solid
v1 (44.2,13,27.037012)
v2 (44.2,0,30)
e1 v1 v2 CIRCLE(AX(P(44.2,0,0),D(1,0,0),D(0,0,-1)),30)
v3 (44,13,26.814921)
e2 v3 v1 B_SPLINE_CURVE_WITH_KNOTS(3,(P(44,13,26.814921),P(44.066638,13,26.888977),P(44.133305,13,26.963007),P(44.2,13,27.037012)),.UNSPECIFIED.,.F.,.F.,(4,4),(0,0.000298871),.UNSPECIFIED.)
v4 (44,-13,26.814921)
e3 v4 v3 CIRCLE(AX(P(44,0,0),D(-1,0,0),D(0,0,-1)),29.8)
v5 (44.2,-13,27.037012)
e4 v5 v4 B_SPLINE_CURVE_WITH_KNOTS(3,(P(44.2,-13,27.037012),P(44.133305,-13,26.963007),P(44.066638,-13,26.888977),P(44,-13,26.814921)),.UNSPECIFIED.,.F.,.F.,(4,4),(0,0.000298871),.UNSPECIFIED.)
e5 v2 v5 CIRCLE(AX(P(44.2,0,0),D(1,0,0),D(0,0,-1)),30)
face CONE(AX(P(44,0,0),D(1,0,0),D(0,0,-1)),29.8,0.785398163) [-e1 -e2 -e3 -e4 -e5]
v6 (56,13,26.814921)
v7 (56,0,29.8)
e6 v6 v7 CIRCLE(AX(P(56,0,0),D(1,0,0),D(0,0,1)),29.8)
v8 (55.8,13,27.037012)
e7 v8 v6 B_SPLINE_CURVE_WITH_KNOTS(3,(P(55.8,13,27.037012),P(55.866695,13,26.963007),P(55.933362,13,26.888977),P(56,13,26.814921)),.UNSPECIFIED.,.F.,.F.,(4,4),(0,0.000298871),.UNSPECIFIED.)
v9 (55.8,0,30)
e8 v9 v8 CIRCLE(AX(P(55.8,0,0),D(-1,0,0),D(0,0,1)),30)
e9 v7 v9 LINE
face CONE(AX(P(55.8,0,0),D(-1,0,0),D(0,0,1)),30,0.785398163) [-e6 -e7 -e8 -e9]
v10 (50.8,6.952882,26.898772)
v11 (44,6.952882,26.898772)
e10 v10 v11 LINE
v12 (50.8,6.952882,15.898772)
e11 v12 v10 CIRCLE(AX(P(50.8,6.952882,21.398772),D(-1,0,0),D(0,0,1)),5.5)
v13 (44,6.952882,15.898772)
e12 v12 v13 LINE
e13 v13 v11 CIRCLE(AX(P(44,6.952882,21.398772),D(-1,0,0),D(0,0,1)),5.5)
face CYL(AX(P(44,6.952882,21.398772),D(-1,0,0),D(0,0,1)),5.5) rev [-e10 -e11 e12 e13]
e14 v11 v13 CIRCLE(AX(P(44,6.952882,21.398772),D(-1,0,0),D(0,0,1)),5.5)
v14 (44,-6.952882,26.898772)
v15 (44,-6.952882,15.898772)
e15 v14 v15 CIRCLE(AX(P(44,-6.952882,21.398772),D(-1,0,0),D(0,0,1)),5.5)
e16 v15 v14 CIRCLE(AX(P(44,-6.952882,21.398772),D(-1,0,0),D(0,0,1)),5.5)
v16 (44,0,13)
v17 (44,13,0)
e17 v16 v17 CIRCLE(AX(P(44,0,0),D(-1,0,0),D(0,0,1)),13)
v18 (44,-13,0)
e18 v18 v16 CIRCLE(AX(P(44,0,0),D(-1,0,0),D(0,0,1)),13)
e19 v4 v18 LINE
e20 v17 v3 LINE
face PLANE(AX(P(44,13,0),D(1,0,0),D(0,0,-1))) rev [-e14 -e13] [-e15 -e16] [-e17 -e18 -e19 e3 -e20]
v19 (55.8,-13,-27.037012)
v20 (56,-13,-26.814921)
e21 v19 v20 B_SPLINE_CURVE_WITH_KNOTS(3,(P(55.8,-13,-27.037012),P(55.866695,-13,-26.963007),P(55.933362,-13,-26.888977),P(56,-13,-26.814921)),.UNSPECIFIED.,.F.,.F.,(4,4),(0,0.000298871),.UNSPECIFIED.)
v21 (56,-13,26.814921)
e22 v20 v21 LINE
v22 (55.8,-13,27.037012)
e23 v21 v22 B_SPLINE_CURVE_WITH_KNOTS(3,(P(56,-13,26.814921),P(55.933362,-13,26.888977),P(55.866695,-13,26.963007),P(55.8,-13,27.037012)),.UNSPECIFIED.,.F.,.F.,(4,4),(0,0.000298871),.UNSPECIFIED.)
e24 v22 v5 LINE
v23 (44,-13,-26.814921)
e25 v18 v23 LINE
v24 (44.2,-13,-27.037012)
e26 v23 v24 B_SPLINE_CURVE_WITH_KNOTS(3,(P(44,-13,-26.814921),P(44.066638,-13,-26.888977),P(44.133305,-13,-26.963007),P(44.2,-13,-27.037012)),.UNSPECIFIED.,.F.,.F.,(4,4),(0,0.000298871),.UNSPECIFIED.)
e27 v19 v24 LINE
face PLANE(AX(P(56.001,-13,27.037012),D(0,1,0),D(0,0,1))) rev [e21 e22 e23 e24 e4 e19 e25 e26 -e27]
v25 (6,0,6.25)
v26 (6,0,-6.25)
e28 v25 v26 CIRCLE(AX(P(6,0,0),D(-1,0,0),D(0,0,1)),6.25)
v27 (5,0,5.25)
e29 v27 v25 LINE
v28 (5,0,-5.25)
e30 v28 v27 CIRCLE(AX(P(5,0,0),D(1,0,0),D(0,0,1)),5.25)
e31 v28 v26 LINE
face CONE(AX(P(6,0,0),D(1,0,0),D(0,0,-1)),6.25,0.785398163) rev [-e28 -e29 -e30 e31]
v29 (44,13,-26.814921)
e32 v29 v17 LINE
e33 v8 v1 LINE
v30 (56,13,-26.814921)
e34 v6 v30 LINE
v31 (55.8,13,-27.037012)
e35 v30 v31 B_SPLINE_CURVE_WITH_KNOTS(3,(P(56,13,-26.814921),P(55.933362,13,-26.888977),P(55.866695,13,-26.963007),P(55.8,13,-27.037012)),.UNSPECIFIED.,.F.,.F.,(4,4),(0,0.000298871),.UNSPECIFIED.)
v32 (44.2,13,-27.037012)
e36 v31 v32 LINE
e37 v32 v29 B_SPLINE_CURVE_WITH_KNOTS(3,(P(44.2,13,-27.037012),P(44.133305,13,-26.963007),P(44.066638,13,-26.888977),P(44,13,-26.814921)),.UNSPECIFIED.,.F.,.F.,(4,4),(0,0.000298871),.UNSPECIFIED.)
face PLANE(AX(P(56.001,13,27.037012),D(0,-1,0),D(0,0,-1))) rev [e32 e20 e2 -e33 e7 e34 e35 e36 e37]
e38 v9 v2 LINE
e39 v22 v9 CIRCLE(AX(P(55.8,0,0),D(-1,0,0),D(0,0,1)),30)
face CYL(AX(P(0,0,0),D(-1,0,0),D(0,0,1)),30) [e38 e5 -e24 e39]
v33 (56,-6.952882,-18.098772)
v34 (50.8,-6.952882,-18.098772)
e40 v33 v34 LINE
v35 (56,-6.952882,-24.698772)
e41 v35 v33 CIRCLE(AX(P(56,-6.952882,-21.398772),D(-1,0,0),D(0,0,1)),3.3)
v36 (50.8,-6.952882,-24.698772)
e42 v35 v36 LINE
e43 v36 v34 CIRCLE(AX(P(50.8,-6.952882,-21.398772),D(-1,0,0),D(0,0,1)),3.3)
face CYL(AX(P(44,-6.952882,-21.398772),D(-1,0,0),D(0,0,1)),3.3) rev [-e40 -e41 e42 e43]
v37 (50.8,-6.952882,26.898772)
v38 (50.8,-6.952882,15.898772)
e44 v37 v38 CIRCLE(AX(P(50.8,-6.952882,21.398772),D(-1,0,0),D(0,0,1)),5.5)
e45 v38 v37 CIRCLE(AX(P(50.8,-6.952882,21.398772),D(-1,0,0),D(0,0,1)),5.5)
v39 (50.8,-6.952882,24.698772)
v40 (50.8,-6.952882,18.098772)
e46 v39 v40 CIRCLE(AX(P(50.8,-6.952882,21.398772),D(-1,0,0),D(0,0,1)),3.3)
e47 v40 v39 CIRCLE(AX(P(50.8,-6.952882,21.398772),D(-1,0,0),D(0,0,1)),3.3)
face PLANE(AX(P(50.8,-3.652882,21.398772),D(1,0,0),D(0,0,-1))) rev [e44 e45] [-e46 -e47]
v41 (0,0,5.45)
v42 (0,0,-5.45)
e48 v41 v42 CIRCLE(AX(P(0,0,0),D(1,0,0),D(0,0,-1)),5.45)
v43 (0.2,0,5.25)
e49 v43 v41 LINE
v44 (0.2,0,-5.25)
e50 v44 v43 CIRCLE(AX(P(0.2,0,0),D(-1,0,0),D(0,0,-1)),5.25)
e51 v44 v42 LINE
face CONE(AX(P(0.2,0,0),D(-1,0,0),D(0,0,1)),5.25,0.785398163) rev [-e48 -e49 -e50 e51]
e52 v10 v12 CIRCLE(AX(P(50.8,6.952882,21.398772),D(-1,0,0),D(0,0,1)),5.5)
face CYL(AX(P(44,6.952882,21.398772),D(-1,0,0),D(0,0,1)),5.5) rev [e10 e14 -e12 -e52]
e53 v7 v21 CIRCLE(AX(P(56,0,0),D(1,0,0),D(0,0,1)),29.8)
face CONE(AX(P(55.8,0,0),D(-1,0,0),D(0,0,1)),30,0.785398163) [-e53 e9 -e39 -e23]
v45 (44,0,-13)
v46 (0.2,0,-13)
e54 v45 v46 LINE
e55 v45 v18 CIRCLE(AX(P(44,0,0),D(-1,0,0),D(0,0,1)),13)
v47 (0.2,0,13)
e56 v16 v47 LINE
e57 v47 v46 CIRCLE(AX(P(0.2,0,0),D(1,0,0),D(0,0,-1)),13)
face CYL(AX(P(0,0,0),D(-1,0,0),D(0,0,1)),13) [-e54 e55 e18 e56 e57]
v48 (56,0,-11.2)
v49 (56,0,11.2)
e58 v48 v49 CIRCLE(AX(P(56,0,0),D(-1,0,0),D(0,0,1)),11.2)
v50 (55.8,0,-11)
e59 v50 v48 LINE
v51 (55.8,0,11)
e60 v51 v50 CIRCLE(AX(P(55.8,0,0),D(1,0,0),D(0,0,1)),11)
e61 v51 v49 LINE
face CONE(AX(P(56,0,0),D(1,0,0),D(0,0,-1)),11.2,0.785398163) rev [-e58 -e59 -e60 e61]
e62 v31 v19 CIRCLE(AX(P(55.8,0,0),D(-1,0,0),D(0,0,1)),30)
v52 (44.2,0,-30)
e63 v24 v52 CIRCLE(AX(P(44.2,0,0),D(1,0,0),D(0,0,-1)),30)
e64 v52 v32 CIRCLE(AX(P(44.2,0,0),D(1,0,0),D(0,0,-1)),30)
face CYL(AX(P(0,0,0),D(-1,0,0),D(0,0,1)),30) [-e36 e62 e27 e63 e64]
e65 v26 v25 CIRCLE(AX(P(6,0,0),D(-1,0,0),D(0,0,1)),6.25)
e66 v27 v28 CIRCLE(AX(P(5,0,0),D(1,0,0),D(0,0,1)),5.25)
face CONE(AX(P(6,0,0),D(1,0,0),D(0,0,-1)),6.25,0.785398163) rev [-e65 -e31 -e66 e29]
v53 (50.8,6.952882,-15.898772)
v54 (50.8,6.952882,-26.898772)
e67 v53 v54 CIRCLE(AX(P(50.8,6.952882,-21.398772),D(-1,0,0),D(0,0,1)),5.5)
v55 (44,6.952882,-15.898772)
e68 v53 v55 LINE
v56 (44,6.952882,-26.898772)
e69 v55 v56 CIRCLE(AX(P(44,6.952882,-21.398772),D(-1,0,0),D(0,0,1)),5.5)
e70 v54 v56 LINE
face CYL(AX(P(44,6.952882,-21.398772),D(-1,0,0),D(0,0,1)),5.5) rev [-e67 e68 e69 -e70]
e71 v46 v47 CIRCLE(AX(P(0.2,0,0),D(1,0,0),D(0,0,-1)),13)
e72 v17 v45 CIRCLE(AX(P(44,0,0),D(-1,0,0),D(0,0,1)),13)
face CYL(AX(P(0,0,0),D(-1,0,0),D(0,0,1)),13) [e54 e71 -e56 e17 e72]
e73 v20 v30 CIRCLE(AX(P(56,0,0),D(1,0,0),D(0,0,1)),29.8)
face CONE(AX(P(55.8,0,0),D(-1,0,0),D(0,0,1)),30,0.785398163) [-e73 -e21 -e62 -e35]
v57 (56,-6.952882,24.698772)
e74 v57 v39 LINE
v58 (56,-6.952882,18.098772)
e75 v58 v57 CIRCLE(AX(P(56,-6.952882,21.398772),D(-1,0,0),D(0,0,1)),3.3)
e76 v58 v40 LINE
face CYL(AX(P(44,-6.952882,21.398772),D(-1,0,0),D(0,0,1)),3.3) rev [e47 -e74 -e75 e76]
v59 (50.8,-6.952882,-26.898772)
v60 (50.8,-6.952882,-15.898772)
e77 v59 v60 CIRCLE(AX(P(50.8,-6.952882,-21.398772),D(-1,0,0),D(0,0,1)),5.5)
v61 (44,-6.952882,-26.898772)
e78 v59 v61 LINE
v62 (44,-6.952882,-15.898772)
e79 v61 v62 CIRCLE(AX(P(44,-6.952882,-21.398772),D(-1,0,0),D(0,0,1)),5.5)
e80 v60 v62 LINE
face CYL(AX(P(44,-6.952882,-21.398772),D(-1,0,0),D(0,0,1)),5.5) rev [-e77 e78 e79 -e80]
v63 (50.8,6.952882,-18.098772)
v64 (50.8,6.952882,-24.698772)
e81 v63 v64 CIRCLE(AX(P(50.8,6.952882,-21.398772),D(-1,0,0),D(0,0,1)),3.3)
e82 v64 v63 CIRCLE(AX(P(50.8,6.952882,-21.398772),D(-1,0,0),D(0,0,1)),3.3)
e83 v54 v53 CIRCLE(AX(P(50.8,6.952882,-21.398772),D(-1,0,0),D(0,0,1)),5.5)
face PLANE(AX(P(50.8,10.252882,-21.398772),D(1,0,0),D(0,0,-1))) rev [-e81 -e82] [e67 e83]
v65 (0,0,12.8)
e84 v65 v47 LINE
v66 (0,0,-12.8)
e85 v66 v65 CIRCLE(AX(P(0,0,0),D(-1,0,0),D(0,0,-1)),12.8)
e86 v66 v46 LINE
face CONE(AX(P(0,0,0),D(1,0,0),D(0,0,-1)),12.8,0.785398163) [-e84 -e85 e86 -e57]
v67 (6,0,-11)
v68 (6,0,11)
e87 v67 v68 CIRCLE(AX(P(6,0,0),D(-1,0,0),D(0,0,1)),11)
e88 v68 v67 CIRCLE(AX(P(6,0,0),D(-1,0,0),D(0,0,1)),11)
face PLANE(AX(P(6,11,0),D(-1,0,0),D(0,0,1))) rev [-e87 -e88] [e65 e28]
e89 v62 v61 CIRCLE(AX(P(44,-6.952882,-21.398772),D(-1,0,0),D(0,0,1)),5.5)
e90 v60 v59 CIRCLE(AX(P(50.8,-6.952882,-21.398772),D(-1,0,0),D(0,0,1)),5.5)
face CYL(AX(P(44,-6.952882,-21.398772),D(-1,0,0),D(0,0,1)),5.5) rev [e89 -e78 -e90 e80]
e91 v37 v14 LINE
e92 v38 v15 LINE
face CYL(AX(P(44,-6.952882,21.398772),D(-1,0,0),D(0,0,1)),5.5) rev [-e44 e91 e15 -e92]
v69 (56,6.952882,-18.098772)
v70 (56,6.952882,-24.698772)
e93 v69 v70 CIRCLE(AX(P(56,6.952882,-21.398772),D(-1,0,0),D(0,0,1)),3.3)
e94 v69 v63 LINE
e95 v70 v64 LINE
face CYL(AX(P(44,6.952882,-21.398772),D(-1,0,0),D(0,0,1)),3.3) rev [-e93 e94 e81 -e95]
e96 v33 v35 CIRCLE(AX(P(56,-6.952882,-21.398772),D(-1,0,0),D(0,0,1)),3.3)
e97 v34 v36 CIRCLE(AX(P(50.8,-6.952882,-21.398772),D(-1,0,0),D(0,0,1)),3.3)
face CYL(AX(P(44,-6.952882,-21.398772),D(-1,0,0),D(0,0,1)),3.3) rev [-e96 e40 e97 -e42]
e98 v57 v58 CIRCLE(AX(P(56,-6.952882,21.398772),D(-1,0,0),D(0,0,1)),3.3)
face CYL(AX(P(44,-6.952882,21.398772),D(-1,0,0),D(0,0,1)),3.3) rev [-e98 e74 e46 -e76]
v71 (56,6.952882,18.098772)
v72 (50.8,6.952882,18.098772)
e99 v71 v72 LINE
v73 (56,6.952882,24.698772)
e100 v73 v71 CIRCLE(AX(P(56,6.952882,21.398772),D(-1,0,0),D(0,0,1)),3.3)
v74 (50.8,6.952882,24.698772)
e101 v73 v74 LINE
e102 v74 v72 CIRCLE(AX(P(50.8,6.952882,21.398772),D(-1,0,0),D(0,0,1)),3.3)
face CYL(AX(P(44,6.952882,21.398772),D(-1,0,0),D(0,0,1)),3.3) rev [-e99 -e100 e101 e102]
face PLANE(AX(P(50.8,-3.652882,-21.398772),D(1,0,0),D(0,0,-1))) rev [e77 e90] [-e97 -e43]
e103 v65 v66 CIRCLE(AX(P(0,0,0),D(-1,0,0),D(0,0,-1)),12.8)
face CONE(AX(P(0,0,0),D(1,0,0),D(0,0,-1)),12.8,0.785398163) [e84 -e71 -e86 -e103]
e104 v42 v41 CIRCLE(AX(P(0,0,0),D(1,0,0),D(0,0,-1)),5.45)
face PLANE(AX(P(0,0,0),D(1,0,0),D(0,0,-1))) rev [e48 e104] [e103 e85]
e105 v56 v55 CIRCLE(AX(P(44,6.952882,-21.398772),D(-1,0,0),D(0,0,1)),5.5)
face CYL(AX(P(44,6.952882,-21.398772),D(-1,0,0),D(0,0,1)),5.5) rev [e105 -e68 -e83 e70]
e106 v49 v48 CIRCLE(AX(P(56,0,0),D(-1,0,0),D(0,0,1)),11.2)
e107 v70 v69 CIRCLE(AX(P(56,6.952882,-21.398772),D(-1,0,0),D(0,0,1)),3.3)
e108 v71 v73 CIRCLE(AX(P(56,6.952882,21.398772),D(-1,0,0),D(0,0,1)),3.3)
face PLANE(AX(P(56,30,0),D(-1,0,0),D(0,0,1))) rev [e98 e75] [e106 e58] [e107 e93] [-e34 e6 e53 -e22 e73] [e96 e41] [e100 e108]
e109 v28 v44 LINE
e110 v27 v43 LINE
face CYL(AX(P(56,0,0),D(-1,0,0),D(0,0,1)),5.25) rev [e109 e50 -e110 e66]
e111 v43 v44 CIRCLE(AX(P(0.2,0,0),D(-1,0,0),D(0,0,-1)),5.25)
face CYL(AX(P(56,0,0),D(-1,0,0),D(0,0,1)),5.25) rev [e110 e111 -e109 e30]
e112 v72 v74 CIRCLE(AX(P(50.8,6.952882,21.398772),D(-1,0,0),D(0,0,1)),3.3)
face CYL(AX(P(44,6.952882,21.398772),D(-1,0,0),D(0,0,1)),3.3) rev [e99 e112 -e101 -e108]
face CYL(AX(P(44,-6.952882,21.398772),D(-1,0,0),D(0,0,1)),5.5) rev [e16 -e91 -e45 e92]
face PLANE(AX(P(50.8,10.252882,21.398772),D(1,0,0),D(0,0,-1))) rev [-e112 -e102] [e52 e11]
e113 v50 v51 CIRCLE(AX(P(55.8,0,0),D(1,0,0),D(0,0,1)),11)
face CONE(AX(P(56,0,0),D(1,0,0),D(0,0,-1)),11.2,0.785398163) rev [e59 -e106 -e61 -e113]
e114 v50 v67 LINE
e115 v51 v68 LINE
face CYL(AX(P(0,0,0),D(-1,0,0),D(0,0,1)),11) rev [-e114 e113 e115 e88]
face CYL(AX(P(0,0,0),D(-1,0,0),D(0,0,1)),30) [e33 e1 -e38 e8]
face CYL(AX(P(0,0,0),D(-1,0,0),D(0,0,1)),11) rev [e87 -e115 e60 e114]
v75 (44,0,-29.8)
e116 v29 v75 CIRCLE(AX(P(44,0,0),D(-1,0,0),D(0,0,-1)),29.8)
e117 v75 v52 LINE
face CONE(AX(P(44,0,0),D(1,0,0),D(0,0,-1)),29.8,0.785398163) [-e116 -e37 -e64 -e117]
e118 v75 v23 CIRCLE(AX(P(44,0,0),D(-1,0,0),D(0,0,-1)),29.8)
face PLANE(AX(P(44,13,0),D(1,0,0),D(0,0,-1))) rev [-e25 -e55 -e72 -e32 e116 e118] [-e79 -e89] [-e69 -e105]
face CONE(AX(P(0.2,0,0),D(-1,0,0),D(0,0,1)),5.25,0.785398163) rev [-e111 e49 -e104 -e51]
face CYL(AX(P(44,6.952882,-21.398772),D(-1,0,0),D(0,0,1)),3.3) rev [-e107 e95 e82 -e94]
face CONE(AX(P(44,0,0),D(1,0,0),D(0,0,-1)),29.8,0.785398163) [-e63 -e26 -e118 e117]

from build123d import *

# Parameters (mm, degrees)
SKETCH2_R                                           = 5.25
CUT_EXTRUDE1_DEPTH                                  = 71.256672281
CUT_EXTRUDE2_REACH                                  = 63.123
HOLE_SIZE_PER_HEX_SOCKET_HEAD_CAP_SCREW_D           = 6.6
HOLE_SIZE_PER_HEX_SOCKET_HEAD_CAP_SCREW_CBORE_D     = 11
HOLE_SIZE_PER_HEX_SOCKET_HEAD_CAP_SCREW_CBORE_DEPTH = 6.8
CHAMFER1_SIZE                                       = 0.2
CHAMFER2_SIZE                                       = 0.2
CHAMFER3_SIZE                                       = 1


with BuildPart() as part:
    # Sketch1 → Revolve1 (revolve)
    with BuildSketch(Plane.XY, mode=Mode.PRIVATE) as revolve1_sk:
        Polygon((0, 0), (0, 13), (44, 13), (44, 30), (56, 30), (56, 11), (6, 11), (6, 0), align=None)
    revolve(revolve1_sk.sketch.rotate(Axis((0, 0, 0), (1, 0, 0)), 90), axis=Axis((0, 0, 0), (1, 0, 0)))

    # Sketch2 → Cut-Extrude1 (cut, through all)
    with BuildSketch(Plane.ZY):
        Circle(SKETCH2_R)
    extrude(amount=-CUT_EXTRUDE1_DEPTH, mode=Mode.SUBTRACT)

    # Sketch3 → Cut-Extrude2 (cut, up to next)
    with BuildSketch(Plane.ZY.offset(-44), mode=Mode.PRIVATE) as cut_extrude2_sk1:
        with BuildLine():
            Line((27.037011669, 13), (-27.037011669, 13))
            ThreePointArc((-27.037011669, 13), (0, 30), (27.037011669, 13))
        make_face()
    cut_extrude2_tool1 = extrude(cut_extrude2_sk1.sketch, amount=-CUT_EXTRUDE2_REACH, mode=Mode.PRIVATE) & part.part
    # Sketch3 → Cut-Extrude2 (cut, up to next)
    with BuildSketch(Plane.ZY.offset(-44), mode=Mode.PRIVATE) as cut_extrude2_sk2:
        with BuildLine():
            Line((27.037011669, -13), (-27.037011669, -13))
            ThreePointArc((-27.037011669, -13), (0, -30), (27.037011669, -13))
        make_face()
    cut_extrude2_tool2 = extrude(cut_extrude2_sk2.sketch, amount=-CUT_EXTRUDE2_REACH, mode=Mode.PRIVATE) & part.part
    add(cut_extrude2_tool1.solids().sort_by_distance((44, 19.998046, 0))[0], mode=Mode.SUBTRACT)
    add(cut_extrude2_tool2.solids().sort_by_distance((44, -19.998046, 0))[0], mode=Mode.SUBTRACT)

    # Hole size per hex socket head cap screw type 1 (through all)
    with Locations(Plane(origin=(44, -6.952882373, 21.398771617), x_dir=(0, 0, -1), z_dir=(-1, 0, 0))):
        with Locations((0, 0), (0, -13.905764746), (42.797543234, -13.905764746), (42.797543234, 0)):
            CounterBoreHole(HOLE_SIZE_PER_HEX_SOCKET_HEAD_CAP_SCREW_D / 2, HOLE_SIZE_PER_HEX_SOCKET_HEAD_CAP_SCREW_CBORE_D / 2, HOLE_SIZE_PER_HEX_SOCKET_HEAD_CAP_SCREW_CBORE_DEPTH)

    # Chamfer1
    chamfer1_edges = [part.edges().sort_by_distance(p)[0] for p in [
        (0, 0, -5.25),
        (56, 0, 30),
        (44, 0, 30),
        (56, 0, -30),
        (44, 0, -30),
        (0, 0, -13),
    ]]
    chamfer(chamfer1_edges, length=CHAMFER1_SIZE)

    # Chamfer2
    chamfer2_edges = [part.edges().sort_by_distance(p)[0] for p in [
        (56, 0, -11),
    ]]
    chamfer(chamfer2_edges, length=CHAMFER2_SIZE)

    # Chamfer3
    chamfer3_edges = [part.edges().sort_by_distance(p)[0] for p in [
        (6, 0, -5.25),
    ]]
    chamfer(chamfer3_edges, length=CHAMFER3_SIZE)


solid = part.part
